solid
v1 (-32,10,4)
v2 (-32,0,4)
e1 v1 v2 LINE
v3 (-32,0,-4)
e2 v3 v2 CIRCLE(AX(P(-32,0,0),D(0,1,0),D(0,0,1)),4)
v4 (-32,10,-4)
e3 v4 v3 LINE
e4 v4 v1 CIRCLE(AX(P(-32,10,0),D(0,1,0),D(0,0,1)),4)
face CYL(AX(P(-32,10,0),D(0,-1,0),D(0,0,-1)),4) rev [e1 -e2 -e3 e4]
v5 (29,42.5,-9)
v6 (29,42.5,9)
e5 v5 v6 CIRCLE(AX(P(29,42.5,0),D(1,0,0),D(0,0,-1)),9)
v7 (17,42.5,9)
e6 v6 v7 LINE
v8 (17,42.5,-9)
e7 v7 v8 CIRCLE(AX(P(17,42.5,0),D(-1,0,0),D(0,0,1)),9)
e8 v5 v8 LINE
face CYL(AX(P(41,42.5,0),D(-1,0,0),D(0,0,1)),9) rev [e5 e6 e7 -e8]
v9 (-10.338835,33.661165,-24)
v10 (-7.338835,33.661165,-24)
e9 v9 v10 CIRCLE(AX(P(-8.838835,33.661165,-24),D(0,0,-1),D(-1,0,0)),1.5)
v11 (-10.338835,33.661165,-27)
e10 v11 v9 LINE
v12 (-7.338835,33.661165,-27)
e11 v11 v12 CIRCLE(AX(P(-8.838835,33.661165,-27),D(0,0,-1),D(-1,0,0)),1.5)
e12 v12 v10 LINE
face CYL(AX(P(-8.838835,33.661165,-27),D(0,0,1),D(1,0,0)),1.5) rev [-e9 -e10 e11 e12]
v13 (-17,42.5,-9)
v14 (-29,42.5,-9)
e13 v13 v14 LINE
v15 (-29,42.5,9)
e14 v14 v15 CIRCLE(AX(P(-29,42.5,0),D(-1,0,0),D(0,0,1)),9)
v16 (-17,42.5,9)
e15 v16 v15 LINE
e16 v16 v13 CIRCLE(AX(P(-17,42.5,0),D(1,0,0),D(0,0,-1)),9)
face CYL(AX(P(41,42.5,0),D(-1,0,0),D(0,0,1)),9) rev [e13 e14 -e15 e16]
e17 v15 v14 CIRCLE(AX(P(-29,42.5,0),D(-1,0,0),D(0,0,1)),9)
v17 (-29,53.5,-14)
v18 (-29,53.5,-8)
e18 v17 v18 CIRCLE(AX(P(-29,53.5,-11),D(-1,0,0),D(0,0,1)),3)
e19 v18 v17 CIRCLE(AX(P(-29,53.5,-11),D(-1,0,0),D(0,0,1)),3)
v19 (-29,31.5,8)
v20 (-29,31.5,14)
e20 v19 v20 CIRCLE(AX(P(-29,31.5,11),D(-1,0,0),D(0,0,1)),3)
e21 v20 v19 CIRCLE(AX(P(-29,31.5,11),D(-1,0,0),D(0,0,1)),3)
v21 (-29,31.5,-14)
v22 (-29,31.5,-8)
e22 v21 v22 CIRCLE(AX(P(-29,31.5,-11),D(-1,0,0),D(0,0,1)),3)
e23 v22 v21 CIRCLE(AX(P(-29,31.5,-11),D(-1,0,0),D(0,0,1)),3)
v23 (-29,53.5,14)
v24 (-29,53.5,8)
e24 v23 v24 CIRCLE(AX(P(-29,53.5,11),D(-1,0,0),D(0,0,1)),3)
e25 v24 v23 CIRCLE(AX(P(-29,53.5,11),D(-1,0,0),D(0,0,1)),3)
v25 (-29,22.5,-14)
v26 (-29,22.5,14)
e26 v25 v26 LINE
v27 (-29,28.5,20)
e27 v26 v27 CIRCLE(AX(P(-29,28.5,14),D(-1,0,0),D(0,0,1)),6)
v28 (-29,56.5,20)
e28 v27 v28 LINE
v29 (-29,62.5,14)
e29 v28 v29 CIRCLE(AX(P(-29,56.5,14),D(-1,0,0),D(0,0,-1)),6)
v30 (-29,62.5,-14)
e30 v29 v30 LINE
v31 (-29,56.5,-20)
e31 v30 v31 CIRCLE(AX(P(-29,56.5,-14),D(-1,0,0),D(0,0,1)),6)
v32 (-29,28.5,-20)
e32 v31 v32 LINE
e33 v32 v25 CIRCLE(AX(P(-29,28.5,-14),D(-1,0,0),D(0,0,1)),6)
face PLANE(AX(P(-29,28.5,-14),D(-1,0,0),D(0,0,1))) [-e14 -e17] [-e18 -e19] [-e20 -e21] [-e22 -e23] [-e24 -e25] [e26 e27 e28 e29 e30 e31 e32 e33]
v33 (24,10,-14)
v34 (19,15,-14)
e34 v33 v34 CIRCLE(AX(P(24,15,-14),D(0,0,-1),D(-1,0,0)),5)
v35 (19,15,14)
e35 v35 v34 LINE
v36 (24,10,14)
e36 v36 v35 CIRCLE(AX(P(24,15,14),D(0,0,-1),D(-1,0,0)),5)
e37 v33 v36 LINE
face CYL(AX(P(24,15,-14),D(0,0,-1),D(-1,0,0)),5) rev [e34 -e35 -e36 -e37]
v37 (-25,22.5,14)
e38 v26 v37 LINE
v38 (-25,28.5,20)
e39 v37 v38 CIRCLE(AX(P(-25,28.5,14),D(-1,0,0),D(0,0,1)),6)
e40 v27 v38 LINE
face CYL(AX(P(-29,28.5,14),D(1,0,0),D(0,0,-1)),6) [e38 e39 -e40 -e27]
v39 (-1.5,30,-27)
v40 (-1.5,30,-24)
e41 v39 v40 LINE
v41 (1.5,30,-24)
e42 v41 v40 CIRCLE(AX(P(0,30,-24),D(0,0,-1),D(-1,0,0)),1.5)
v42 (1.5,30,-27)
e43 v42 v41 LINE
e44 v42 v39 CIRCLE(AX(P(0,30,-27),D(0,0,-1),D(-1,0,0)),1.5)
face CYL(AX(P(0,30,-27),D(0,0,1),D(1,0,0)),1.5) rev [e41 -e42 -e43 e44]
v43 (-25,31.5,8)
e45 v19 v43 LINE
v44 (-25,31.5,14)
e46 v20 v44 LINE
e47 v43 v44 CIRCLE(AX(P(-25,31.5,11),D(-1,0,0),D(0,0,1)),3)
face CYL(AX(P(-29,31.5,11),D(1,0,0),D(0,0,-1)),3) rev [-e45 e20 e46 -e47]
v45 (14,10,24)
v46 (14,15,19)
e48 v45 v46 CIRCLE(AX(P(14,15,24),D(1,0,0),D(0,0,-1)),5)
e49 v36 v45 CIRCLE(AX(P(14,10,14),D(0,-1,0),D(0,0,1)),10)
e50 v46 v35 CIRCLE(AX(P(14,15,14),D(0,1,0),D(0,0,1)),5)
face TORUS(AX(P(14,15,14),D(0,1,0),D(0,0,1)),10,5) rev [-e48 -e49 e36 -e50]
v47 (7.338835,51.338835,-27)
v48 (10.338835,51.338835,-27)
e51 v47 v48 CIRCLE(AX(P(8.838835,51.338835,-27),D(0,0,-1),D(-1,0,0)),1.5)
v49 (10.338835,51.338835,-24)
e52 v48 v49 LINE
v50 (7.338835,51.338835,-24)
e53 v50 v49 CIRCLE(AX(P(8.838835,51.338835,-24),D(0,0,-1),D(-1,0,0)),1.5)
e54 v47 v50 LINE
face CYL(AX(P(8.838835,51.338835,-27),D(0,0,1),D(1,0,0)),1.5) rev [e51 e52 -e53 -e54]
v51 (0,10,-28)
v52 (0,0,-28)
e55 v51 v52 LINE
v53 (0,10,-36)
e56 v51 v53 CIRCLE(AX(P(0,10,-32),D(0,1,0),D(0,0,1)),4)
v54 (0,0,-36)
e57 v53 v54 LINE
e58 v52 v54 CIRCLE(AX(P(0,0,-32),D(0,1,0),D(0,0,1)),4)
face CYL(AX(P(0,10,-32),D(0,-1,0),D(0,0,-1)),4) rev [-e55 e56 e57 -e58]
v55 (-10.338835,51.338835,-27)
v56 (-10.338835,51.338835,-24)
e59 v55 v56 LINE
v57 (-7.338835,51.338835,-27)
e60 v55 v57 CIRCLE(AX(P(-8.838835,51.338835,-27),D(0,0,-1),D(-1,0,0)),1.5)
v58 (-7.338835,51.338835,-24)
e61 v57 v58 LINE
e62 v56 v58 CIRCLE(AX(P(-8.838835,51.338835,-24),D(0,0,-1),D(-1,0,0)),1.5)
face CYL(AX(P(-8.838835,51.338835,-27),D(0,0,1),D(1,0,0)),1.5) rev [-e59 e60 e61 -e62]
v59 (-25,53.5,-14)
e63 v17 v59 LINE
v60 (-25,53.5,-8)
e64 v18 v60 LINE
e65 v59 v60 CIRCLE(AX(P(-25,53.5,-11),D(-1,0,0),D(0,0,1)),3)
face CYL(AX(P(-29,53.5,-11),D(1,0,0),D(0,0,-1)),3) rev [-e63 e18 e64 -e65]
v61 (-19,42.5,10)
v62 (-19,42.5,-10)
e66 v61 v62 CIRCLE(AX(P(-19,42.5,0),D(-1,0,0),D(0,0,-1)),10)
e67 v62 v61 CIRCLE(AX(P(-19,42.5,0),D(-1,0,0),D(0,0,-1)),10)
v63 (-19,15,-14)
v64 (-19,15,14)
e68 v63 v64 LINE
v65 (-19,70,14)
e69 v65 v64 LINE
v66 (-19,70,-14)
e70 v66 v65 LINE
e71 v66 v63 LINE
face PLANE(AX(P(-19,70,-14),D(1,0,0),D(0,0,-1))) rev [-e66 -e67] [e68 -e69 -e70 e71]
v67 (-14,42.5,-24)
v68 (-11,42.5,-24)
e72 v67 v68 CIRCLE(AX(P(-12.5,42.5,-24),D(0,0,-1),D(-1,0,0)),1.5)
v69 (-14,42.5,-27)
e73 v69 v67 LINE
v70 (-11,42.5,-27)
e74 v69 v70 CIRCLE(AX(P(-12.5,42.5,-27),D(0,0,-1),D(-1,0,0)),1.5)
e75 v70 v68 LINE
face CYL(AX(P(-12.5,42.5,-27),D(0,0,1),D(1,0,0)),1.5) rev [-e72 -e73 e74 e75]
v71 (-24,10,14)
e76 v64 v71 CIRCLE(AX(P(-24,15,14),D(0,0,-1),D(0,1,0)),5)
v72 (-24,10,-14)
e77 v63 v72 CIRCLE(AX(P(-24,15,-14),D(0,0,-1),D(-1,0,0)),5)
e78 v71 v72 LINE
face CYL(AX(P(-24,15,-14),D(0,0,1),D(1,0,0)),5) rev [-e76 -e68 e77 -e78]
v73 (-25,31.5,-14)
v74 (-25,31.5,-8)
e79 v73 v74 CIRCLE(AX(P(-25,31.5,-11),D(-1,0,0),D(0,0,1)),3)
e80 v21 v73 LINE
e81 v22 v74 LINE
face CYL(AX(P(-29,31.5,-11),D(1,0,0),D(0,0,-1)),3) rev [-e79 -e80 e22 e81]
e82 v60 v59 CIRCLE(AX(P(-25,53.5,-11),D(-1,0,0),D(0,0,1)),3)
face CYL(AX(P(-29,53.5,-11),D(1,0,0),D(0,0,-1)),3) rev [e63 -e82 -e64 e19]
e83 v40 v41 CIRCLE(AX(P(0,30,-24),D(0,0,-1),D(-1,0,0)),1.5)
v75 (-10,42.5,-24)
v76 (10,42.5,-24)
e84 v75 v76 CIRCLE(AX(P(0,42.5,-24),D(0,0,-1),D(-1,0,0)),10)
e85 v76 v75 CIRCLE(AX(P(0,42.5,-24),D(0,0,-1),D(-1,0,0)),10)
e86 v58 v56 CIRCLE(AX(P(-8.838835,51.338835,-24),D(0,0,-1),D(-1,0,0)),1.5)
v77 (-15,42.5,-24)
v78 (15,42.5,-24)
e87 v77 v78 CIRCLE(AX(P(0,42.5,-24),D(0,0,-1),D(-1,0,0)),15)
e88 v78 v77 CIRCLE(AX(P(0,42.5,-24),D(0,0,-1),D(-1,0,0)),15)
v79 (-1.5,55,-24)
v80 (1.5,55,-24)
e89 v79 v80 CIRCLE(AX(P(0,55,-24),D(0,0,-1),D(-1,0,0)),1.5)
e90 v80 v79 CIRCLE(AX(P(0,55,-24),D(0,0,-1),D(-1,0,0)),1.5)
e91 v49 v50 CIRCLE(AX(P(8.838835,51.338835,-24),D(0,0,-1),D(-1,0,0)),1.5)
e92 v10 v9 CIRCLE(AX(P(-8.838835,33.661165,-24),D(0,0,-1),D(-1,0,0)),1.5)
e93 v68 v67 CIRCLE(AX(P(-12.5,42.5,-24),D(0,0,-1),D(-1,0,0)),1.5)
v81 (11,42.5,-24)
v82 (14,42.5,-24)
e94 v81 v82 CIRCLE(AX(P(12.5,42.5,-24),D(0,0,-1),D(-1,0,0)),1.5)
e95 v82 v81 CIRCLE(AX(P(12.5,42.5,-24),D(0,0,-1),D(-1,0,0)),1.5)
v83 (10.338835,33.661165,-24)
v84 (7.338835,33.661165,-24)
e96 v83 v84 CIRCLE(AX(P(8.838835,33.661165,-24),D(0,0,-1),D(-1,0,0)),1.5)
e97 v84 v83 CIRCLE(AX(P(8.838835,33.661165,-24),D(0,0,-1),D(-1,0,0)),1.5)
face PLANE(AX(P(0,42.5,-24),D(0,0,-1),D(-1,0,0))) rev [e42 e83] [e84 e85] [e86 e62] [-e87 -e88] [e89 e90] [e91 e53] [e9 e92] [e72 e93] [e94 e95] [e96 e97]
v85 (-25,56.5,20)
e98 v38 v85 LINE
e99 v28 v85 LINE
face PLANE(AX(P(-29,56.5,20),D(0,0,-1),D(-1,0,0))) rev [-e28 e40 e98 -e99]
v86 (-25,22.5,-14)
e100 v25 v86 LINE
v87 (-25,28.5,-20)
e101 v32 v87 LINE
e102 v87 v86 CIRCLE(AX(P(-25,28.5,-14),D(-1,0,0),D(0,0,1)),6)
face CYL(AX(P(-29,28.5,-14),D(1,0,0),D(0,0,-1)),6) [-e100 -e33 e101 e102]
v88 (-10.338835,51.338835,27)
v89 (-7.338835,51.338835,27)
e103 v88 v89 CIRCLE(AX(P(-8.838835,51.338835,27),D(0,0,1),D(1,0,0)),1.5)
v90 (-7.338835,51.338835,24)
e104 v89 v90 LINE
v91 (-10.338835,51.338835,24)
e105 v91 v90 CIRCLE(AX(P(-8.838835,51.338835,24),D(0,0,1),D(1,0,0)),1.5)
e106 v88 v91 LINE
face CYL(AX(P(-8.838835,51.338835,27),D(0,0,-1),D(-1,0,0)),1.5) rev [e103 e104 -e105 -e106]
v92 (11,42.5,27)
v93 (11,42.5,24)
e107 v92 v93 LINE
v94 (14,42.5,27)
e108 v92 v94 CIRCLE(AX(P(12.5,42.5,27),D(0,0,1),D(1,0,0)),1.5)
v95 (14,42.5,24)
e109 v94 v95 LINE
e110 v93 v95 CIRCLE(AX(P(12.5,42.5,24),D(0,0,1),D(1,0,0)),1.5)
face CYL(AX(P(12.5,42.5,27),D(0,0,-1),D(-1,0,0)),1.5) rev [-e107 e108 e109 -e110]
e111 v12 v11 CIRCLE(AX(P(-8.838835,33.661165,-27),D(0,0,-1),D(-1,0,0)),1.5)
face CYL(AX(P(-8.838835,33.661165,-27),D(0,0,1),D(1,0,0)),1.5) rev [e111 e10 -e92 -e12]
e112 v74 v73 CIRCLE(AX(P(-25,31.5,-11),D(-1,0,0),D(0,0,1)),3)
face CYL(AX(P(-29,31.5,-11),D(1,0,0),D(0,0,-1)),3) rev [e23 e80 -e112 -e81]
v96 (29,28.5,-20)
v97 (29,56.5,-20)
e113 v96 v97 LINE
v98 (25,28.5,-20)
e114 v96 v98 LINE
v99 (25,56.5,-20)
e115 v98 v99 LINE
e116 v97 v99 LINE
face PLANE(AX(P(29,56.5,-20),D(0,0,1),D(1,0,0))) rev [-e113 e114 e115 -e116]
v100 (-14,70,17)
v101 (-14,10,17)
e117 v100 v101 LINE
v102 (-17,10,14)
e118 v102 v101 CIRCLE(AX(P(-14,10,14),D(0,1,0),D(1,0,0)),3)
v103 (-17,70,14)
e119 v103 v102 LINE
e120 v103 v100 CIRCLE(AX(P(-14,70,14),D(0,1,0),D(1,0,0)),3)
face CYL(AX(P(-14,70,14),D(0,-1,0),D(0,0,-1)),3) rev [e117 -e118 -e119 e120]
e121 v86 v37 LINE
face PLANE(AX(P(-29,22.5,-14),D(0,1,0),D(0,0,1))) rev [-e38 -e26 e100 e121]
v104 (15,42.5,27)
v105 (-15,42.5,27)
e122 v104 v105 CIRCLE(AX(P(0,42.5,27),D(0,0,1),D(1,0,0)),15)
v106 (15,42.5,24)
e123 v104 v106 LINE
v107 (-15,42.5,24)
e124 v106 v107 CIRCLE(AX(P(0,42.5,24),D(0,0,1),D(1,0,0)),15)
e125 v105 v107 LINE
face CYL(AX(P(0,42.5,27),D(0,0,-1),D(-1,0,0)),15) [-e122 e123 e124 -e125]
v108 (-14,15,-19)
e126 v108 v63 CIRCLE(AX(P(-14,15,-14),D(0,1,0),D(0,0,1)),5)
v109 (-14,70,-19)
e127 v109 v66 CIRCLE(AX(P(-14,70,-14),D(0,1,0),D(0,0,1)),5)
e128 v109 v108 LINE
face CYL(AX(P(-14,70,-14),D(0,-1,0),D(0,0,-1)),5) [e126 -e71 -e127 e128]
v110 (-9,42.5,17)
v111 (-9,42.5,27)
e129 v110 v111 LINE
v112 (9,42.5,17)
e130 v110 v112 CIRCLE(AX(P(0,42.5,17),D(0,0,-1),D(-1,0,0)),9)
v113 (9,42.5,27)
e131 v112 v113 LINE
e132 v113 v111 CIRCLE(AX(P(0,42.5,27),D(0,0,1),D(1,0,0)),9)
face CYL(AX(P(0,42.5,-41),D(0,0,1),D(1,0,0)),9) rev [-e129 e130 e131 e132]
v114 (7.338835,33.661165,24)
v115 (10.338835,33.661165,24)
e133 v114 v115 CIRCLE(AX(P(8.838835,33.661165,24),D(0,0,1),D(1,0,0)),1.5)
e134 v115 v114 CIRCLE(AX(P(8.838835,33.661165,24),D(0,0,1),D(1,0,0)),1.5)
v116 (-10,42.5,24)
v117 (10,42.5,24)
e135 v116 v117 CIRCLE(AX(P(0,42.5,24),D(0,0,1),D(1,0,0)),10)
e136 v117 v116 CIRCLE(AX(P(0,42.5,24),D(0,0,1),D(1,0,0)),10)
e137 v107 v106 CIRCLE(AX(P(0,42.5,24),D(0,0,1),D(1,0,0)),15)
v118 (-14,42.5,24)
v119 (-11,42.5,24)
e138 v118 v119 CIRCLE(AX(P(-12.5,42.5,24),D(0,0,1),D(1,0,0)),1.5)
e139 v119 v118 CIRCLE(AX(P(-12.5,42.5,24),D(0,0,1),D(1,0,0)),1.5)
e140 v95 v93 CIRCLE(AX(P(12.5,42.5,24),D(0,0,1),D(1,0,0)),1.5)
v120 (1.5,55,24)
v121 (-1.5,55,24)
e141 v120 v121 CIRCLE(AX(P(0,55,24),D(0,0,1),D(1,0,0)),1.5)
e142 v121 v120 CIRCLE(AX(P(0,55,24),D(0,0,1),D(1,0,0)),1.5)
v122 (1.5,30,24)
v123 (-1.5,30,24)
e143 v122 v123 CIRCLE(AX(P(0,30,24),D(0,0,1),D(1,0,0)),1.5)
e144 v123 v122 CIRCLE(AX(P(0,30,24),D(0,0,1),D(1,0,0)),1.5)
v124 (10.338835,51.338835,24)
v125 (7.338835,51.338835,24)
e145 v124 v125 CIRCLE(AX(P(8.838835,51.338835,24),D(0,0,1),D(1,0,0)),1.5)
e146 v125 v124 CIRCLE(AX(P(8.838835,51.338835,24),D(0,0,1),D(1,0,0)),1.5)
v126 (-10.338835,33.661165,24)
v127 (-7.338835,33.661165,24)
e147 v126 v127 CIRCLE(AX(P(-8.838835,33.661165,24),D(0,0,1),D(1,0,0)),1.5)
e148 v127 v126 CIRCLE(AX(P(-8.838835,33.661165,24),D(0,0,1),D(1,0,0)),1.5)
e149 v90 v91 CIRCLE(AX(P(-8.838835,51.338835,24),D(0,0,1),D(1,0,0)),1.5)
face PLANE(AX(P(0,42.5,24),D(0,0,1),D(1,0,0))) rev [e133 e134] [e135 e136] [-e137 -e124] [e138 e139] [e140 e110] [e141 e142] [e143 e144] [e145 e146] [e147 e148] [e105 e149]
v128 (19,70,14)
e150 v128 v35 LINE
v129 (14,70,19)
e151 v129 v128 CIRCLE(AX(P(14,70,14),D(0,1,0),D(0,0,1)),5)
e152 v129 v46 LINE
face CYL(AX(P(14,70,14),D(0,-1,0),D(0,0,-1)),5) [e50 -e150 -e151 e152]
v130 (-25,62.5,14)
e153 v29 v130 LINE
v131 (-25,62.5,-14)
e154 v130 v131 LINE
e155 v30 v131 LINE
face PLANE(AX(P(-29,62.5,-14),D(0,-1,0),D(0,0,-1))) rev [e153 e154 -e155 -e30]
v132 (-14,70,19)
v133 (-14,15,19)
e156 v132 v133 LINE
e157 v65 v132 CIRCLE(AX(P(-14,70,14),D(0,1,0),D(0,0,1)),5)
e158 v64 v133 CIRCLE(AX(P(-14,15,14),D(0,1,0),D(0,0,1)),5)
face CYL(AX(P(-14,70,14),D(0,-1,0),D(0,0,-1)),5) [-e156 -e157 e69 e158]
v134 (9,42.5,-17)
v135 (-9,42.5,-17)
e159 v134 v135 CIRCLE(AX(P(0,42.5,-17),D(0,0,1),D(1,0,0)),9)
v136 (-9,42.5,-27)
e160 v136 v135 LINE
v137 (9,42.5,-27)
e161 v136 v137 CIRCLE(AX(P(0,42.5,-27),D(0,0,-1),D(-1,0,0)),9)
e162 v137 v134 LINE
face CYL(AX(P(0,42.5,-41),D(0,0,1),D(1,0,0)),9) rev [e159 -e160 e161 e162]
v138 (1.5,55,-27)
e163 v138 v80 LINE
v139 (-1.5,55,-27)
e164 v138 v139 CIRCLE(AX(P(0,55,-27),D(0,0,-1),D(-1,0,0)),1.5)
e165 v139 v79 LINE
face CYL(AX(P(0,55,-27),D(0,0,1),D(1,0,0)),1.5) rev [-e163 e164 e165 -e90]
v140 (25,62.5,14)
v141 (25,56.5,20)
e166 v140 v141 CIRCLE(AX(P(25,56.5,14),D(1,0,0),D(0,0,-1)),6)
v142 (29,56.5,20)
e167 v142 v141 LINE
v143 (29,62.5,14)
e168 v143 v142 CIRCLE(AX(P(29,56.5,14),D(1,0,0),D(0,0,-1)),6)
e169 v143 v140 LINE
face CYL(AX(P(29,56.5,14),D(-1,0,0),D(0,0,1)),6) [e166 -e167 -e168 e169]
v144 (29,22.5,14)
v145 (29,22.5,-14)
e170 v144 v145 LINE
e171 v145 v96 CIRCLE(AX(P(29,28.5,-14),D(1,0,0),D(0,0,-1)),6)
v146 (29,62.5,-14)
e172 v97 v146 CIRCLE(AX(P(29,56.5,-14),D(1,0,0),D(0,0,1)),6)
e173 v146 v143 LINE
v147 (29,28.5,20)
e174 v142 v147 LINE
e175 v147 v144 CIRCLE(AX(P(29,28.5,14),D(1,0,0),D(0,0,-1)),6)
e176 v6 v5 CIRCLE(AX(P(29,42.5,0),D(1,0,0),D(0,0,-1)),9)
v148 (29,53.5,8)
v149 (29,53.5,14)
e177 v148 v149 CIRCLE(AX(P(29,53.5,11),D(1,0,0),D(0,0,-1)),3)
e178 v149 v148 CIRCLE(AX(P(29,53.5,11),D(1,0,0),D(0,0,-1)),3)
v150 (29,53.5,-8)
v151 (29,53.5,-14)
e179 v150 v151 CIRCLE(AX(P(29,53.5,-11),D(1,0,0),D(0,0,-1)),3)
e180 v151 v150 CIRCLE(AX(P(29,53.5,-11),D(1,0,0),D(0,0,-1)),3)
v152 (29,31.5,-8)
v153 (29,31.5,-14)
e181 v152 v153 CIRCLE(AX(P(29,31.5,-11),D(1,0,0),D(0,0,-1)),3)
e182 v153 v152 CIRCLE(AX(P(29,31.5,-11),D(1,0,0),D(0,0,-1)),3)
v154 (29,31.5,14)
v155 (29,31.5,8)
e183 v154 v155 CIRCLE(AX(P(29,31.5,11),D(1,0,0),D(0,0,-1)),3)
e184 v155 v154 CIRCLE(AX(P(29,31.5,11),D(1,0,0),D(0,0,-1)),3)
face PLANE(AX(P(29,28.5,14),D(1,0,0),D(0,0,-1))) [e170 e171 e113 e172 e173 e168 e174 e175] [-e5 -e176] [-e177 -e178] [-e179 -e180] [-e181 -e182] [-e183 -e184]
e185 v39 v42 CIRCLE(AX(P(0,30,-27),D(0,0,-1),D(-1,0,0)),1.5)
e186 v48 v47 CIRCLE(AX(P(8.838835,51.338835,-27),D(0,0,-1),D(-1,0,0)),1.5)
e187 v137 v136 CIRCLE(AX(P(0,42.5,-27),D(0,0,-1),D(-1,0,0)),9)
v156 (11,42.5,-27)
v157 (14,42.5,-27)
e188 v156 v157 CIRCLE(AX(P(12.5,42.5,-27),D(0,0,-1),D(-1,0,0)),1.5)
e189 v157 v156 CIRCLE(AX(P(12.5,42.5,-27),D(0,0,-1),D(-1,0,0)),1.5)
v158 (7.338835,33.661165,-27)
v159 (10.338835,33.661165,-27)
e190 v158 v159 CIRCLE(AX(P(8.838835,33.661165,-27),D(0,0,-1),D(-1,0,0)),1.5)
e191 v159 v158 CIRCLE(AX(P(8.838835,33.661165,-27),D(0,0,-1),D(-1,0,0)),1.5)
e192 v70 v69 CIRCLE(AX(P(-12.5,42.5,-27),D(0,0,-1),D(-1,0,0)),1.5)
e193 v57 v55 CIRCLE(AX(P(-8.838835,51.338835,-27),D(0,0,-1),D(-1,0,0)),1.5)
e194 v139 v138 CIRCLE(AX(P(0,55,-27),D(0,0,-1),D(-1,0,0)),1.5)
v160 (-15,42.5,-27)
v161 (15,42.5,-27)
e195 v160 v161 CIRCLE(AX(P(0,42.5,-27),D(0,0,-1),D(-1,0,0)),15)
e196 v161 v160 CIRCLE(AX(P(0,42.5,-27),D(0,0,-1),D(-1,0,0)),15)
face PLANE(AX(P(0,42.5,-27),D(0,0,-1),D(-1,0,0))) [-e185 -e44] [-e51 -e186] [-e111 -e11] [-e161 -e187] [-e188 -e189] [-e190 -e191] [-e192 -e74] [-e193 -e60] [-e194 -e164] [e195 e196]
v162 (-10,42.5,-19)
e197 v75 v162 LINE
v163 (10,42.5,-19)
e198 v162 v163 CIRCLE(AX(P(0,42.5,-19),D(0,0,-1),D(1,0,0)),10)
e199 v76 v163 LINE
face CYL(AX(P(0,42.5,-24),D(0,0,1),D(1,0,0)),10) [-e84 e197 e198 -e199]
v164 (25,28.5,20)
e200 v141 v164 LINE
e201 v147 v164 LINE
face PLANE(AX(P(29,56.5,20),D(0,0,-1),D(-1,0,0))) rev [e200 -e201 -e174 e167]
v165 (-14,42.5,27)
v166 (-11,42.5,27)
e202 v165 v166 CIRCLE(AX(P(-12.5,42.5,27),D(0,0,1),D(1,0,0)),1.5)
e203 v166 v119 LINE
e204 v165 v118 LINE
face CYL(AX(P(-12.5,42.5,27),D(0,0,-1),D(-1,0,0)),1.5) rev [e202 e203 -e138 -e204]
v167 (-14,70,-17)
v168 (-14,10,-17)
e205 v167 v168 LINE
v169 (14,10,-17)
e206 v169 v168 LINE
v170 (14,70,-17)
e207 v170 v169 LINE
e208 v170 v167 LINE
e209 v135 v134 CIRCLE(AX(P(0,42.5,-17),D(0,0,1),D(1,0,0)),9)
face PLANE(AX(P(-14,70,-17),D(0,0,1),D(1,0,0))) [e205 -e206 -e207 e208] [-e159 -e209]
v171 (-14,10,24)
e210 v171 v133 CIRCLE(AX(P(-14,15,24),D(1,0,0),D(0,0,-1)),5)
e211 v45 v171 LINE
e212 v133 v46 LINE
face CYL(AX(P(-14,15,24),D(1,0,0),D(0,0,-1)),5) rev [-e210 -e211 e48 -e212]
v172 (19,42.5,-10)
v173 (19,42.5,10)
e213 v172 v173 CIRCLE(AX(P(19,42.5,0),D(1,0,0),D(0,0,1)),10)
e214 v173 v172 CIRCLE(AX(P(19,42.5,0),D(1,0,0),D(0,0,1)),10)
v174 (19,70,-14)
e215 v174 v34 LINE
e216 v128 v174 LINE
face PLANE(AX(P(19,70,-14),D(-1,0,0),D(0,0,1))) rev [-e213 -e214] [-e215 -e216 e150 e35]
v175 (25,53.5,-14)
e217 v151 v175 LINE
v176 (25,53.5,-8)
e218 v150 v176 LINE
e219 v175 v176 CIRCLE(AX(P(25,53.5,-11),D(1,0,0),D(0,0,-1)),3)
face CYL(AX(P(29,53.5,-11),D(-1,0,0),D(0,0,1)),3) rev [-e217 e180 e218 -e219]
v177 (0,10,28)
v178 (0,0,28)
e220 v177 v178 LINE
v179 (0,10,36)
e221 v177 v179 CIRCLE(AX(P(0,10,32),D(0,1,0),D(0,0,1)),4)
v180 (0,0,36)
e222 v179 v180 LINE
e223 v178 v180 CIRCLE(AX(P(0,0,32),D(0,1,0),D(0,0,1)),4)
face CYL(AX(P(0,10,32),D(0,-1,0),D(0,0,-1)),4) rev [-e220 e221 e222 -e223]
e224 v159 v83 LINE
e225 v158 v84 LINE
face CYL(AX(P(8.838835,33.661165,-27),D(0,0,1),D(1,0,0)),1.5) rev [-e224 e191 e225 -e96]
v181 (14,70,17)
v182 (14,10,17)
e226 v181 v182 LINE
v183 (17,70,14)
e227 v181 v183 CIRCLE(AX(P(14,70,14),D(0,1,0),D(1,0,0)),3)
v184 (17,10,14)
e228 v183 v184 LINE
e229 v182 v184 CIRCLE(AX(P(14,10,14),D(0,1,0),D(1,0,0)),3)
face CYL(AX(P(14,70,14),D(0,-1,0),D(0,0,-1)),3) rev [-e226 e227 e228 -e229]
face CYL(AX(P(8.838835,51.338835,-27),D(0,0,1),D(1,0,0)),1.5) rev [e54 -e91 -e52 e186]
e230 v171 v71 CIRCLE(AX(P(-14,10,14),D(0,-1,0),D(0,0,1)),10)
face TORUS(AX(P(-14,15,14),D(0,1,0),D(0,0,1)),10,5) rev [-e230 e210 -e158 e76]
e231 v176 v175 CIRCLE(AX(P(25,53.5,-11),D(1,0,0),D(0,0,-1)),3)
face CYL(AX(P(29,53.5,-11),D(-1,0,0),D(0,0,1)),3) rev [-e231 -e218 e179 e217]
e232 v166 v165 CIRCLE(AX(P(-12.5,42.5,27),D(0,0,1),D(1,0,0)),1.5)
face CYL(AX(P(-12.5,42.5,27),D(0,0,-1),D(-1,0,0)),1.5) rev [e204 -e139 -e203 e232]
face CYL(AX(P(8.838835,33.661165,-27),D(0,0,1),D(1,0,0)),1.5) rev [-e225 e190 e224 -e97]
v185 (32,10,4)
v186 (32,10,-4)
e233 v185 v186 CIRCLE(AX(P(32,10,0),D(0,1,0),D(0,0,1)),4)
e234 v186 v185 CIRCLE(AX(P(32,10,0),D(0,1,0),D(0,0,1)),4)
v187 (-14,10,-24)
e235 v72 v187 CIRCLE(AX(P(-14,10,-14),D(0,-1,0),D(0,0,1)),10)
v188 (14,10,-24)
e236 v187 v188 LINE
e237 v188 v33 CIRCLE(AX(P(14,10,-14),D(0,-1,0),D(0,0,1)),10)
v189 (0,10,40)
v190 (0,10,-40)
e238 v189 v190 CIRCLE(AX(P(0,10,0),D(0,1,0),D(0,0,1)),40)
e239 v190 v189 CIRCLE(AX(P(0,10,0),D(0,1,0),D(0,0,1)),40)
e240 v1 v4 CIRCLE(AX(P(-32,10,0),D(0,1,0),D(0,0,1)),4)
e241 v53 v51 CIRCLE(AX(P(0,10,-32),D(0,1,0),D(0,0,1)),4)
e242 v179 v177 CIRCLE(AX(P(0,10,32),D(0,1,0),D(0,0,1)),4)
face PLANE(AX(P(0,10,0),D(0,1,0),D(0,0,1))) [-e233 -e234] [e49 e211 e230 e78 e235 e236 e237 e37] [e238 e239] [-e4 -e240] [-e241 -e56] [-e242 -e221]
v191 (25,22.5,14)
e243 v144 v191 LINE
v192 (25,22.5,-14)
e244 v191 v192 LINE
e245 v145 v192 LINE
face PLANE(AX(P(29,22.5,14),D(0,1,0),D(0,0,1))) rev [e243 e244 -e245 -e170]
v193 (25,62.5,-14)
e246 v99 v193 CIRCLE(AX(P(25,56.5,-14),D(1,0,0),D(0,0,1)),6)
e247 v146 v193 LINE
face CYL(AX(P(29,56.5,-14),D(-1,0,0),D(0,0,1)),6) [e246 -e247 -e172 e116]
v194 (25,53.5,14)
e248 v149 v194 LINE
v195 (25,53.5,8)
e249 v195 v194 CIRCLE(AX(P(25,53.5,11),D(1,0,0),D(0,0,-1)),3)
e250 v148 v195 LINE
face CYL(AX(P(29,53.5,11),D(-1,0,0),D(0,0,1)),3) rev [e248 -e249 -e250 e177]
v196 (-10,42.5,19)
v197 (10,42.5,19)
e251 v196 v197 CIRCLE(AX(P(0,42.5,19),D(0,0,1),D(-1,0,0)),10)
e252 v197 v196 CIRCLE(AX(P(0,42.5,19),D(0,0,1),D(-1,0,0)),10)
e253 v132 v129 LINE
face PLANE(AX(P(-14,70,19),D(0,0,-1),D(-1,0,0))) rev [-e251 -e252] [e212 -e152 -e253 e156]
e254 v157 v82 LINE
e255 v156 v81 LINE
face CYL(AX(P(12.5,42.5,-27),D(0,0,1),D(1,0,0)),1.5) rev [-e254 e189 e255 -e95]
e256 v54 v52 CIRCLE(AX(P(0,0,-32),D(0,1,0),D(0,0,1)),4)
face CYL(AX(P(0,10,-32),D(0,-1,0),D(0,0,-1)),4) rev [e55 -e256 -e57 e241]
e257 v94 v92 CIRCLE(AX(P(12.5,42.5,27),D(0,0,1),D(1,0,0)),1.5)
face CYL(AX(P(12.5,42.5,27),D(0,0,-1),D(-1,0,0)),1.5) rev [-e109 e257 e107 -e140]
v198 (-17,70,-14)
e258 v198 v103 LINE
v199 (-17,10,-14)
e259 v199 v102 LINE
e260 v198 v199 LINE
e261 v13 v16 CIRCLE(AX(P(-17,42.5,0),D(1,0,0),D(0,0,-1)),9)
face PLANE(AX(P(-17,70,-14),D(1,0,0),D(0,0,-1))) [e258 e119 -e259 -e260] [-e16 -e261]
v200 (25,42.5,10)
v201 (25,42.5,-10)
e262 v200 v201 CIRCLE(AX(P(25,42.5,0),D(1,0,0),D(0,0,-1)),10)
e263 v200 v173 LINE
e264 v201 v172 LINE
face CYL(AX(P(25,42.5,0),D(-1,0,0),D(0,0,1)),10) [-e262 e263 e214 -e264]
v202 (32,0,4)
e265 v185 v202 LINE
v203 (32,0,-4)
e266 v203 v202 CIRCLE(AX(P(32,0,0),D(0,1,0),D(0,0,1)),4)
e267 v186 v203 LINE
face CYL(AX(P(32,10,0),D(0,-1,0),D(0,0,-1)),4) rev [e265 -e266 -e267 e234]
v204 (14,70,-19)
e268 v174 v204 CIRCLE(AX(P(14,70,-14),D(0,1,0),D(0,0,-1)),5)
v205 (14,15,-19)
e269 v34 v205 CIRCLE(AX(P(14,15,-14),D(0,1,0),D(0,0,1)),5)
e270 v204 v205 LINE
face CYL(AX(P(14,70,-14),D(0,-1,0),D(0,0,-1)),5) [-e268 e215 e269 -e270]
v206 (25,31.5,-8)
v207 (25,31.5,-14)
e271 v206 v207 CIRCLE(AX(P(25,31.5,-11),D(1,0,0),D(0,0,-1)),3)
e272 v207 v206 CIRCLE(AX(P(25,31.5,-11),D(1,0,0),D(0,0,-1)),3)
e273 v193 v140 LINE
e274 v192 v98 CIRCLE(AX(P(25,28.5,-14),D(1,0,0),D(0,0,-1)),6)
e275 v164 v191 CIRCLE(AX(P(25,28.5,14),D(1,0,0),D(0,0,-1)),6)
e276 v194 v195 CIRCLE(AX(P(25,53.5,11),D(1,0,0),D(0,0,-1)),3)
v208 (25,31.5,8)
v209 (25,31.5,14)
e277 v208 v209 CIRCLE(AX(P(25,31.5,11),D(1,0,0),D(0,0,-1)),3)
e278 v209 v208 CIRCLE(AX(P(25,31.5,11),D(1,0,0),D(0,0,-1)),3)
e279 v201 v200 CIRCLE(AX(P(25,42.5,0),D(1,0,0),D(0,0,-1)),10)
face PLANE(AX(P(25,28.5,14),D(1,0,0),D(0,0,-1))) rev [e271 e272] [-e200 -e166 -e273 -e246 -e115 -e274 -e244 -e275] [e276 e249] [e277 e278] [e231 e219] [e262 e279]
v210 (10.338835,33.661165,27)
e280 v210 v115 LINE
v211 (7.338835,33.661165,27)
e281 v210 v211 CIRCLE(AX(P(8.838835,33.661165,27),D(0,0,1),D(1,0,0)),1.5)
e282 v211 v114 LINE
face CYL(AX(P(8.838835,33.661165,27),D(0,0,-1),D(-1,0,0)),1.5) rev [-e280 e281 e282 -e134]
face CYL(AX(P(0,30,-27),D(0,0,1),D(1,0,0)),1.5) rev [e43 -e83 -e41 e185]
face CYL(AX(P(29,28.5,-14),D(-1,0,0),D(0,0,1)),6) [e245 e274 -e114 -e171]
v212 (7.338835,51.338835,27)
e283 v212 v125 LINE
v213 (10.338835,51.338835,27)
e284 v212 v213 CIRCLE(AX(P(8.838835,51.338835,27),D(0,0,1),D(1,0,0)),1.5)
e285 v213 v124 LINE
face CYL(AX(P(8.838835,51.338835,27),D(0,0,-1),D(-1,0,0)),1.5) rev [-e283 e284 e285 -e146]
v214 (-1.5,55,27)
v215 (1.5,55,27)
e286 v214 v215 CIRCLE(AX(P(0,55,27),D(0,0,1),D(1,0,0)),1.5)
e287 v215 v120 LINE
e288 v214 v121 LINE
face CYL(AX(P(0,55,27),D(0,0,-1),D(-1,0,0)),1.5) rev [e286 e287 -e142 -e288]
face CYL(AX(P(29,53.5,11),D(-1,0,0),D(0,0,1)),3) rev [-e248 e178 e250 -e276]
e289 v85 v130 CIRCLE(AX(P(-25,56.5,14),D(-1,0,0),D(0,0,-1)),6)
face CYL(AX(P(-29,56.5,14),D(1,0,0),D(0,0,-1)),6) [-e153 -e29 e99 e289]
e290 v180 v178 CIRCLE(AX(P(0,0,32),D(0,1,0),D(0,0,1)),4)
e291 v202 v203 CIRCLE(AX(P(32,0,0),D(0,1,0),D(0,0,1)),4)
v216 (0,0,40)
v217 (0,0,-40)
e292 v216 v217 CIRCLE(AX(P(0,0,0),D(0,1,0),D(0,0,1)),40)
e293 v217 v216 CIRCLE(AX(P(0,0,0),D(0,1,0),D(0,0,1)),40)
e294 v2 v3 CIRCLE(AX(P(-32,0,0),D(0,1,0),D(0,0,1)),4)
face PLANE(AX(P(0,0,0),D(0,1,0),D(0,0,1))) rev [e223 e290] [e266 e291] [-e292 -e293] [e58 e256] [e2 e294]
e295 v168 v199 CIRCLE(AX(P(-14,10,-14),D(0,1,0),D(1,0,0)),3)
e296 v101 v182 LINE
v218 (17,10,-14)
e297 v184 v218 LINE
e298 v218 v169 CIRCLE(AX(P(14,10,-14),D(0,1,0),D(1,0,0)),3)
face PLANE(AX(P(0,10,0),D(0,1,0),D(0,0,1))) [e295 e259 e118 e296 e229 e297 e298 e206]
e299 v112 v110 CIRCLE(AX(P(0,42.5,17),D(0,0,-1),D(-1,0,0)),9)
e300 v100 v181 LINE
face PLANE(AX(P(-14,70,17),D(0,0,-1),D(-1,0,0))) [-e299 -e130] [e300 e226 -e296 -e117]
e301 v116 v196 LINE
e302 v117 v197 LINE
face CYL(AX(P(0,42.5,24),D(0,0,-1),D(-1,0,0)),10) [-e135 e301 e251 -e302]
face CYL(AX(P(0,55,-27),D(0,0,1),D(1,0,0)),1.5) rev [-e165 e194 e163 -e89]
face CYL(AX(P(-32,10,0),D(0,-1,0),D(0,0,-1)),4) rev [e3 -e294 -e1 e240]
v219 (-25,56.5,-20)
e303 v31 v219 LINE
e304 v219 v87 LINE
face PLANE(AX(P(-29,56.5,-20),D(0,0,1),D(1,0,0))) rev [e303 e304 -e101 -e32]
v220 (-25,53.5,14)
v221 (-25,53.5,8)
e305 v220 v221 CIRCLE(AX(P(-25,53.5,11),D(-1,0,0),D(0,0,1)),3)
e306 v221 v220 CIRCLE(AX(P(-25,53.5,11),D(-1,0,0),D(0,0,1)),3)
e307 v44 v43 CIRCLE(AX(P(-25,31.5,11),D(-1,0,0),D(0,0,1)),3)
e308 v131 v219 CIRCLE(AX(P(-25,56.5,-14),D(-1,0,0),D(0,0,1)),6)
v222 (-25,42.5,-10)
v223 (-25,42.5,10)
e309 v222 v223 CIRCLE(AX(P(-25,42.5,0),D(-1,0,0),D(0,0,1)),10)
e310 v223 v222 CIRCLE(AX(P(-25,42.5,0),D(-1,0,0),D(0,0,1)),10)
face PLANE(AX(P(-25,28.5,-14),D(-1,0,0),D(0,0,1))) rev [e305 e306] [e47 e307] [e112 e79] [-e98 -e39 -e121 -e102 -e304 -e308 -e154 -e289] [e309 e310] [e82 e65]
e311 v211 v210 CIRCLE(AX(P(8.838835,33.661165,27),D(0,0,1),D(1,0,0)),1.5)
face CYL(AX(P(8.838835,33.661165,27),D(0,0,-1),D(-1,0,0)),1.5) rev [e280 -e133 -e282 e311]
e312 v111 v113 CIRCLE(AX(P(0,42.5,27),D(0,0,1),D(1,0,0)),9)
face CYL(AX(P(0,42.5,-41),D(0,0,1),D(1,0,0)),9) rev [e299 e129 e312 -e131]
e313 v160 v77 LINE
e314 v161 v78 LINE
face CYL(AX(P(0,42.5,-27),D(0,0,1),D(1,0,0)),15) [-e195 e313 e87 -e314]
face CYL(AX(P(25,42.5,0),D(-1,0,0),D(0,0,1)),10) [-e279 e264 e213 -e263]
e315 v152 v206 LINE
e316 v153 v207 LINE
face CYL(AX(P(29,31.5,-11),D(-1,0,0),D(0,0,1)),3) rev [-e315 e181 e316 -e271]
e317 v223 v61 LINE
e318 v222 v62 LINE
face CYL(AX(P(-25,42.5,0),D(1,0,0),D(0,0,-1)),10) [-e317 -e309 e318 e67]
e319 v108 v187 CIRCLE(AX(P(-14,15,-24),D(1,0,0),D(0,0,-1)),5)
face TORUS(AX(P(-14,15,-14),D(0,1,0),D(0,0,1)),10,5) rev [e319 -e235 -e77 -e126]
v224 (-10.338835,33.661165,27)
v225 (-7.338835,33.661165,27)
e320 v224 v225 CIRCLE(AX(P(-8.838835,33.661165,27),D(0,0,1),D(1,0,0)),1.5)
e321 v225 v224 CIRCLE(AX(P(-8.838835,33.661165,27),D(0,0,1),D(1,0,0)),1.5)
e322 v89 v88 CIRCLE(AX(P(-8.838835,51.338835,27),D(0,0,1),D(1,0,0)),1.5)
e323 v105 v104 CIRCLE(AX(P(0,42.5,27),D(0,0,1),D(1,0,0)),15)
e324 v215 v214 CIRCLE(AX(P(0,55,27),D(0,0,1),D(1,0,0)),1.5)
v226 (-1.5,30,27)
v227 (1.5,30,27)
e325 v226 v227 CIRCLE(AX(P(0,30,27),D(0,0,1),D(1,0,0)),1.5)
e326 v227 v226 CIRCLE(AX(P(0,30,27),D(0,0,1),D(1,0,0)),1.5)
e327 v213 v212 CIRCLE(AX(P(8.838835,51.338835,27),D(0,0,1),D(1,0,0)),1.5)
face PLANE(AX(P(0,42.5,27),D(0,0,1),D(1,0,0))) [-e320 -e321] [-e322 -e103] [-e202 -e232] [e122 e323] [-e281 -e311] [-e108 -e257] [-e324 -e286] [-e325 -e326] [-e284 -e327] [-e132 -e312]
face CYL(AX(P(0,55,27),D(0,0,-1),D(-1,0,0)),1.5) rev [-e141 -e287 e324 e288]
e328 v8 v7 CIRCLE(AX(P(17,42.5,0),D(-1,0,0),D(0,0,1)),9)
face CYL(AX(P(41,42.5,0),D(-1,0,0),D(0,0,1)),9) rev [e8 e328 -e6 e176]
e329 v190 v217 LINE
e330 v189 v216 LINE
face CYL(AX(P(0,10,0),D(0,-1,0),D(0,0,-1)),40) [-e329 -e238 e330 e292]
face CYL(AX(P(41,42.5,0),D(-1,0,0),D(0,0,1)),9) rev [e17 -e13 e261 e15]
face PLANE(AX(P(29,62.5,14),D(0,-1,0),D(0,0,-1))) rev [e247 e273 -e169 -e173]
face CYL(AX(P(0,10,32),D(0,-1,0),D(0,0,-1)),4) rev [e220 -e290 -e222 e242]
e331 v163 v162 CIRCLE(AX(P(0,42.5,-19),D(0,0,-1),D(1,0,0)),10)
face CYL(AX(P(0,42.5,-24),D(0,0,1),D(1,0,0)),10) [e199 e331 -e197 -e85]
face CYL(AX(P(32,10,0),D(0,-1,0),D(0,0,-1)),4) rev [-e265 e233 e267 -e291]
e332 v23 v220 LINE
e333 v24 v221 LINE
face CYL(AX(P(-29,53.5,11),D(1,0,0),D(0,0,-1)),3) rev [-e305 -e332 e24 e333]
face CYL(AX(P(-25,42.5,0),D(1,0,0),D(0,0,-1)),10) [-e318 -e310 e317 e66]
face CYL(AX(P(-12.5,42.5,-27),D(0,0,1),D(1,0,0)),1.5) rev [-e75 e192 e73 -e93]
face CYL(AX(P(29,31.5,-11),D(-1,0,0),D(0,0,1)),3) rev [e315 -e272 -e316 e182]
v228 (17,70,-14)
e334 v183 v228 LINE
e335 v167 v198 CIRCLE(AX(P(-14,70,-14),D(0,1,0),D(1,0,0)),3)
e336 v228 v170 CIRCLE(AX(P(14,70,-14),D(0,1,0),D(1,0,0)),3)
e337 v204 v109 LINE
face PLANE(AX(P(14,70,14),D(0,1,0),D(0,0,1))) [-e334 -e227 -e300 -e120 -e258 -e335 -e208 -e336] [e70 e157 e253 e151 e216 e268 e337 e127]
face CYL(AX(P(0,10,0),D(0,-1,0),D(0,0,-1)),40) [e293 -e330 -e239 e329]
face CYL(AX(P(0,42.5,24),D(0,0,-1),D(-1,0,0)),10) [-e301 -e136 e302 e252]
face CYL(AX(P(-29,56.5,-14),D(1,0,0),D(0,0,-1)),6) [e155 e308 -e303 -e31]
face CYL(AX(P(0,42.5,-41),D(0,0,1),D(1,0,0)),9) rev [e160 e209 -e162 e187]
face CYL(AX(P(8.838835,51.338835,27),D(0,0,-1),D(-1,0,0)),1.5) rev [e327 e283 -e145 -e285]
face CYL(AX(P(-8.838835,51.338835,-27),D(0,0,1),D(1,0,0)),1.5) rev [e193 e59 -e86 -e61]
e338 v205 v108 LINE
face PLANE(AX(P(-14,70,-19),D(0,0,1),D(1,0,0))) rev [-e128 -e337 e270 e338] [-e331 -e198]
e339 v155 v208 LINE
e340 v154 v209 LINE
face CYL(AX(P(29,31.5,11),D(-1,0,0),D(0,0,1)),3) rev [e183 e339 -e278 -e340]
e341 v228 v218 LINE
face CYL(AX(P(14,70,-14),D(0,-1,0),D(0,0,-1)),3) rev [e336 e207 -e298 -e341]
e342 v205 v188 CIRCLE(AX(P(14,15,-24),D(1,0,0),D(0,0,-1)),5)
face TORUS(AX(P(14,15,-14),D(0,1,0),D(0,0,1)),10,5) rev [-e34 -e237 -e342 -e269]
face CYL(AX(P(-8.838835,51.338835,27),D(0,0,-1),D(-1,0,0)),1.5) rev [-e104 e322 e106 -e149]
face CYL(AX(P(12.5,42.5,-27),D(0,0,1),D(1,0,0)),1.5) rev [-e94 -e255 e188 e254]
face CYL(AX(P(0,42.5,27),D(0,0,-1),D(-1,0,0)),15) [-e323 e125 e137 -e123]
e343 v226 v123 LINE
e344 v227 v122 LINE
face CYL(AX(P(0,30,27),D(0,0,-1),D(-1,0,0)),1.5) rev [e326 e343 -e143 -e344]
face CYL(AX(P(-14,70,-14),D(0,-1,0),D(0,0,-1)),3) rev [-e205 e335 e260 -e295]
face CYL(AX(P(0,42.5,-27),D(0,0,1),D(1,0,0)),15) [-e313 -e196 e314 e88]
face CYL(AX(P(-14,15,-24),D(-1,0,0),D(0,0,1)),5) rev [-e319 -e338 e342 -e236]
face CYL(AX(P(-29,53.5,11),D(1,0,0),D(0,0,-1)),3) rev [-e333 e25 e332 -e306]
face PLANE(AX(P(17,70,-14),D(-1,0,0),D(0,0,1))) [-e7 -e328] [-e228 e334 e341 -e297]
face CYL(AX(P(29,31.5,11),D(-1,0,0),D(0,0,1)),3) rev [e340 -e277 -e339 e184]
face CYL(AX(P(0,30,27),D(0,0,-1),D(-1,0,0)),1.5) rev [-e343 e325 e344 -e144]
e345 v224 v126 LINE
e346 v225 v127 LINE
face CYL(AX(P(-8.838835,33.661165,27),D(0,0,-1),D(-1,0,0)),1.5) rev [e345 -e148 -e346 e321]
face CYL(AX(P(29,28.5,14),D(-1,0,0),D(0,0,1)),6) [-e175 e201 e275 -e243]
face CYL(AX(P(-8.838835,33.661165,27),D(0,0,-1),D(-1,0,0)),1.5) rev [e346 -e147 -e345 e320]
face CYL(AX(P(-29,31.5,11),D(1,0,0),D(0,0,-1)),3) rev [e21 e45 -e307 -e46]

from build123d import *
from build123d.topology import SkipClean

# Parameters (mm, degrees)
BASE_FLANGE_SKETCH_R           = 40
BASE_FLANGE_SKETCH_R_2         = 4
BASE_FLANGE_80_DEPTH           = 10
SQUARE_BODY_38X38_WALL_2_DEPTH = 60
BODY_TO_FLANGE_FILLET_R5_R     = 5
CROSS_BORE_A_SKETCH_R          = 9
CROSS_BORE_A_18_DEPTH          = 60
CROSS_BORE_B_SKETCH_R          = 9
CROSS_BORE_B_18_DEPTH          = 60
PORT_START                     = 5
PORT_A1_STUB_SKETCH_R          = 10
PORT_A1_STUB_SKETCH_R_2        = 9
PORT_A1_STUB_18_DEPTH          = 5
ROUND_START                    = 3
ROUND_FLANGE_A1_SKETCH_R       = 15
ROUND_FLANGE_A1_SKETCH_R_2     = 9
ROUND_FLANGE_A1_SKETCH_R_3     = 1.5
ROUND_FLANGE_A1_30_DEPTH       = 3
PORT_A2_STUB_SKETCH_R          = 10
PORT_A2_STUB_SKETCH_R_2        = 9
PORT_A2_STUB_18_DEPTH          = 5
ROUND_FLANGE_A2_SKETCH_R       = 15
ROUND_FLANGE_A2_SKETCH_R_2     = 9
ROUND_FLANGE_A2_SKETCH_R_3     = 1.5
ROUND_FLANGE_A2_30_DEPTH       = 3
PORT_START_2                   = 6
PORT_B1_STUB_SKETCH_R          = 10
PORT_B1_STUB_SKETCH_R_2        = 9
PORT_B1_STUB_18_DEPTH          = 6
SQUARE_START                   = 4
SQUARE_FLANGE_B1_SKETCH_R      = 9
SQUARE_FLANGE_B1_SKETCH_R_2    = 3
SQUARE_FLANGE_B1_40X40_DEPTH   = 4
PORT_B2_STUB_SKETCH_R          = 10
PORT_B2_STUB_SKETCH_R_2        = 9
PORT_B2_STUB_18_DEPTH          = 6
SQUARE_FLANGE_B2_SKETCH_R      = 9
SQUARE_FLANGE_B2_SKETCH_R_2    = 3
SQUARE_FLANGE_B2_40X40_DEPTH   = 4


with BuildPart() as part:
    # Base Flange Sketch → Base Flange Ø80 (new body)
    with BuildSketch(Plane(origin=(0, 0, 0), x_dir=(1, 0, 0), z_dir=(0, 1, 0))):
        with Locations(Location((0, 0, 0), (0, 0, 270))):
            Circle(BASE_FLANGE_SKETCH_R)
        with Locations(Location((0, 32, 0), (0, 0, 270))):
            Circle(BASE_FLANGE_SKETCH_R_2, mode=Mode.SUBTRACT)
        with Locations(Location((32, 0, 0), (0, 0, 270))):
            Circle(BASE_FLANGE_SKETCH_R_2, mode=Mode.SUBTRACT)
        with Locations(Location((0, -32, 0), (0, 0, 270))):
            Circle(BASE_FLANGE_SKETCH_R_2, mode=Mode.SUBTRACT)
        with Locations(Location((-32, 0, 0), (0, 0, 270))):
            Circle(BASE_FLANGE_SKETCH_R_2, mode=Mode.SUBTRACT)
    extrude(amount=BASE_FLANGE_80_DEPTH)

    # Square Body Sketch → Square Body 38x38 Wall 2 (add)
    with BuildSketch(Plane(origin=(0, 10, 0), x_dir=(1, 0, 0), z_dir=(0, 1, 0))):
        with BuildLine():
            Line((19, 14), (19, -14))
            ThreePointArc((19, -14), (17.535533906, -17.535533906), (14, -19))
            Line((14, -19), (-14, -19))
            ThreePointArc((-14, -19), (-17.535533906, -17.535533906), (-19, -14))
            Line((-19, -14), (-19, 14))
            ThreePointArc((-19, 14), (-17.535533906, 17.535533906), (-14, 19))
            Line((-14, 19), (14, 19))
            ThreePointArc((14, 19), (17.535533906, 17.535533906), (19, 14))
        make_face()
        with BuildLine():
            Line((17, 14), (17, -14))
            ThreePointArc((17, -14), (16.121320344, -16.121320344), (14, -17))
            Line((14, -17), (-14, -17))
            ThreePointArc((-14, -17), (-16.121320344, -16.121320344), (-17, -14))
            Line((-17, -14), (-17, 14))
            ThreePointArc((-17, 14), (-16.121320344, 16.121320344), (-14, 17))
            Line((-14, 17), (14, 17))
            ThreePointArc((14, 17), (16.121320344, 16.121320344), (17, 14))
        make_face(mode=Mode.SUBTRACT)
    extrude(amount=SQUARE_BODY_38X38_WALL_2_DEPTH)

    # Body to Flange Fillet R5
    body_to_flange_fillet_r5_edges = [part.edges().sort_by_distance(p)[0] for p in [
        (17.535533906, 10, 17.535533906),
        (19, 10, 0),
        (17.535533906, 10, -17.535533906),
        (0, 10, -19),
        (-17.535533906, 10, -17.535533906),
        (-19, 10, 0),
        (-17.535533906, 10, 17.535533906),
        (0, 10, 19),
    ]]
    fillet(body_to_flange_fillet_r5_edges, radius=BODY_TO_FLANGE_FILLET_R5_R)

    # Cross Bore A Sketch → Cross Bore A Ø18 (cut)
    with BuildSketch(Plane.XY.offset(19)):
        with Locations((0, 42.5)):
            Circle(CROSS_BORE_A_SKETCH_R)
    extrude(amount=-CROSS_BORE_A_18_DEPTH, mode=Mode.SUBTRACT)

    # Cross Bore B Sketch → Cross Bore B Ø18 (cut)
    with BuildSketch(Plane.ZY.offset(19)):
        with Locations((0, 42.5)):
            Circle(CROSS_BORE_B_SKETCH_R)
    extrude(amount=-CROSS_BORE_B_18_DEPTH, mode=Mode.SUBTRACT)

    # Port A1 Stub Sketch → Port A1 Stub Ø18 (add)
    with BuildSketch(Plane.XY.offset(19).offset(PORT_START)):
        with Locations((0, 42.5)):
            Circle(PORT_A1_STUB_SKETCH_R)
        with Locations((0, 42.5)):
            Circle(PORT_A1_STUB_SKETCH_R_2, mode=Mode.SUBTRACT)
    extrude(amount=-PORT_A1_STUB_18_DEPTH)

    # Round Flange A1 Sketch → Round Flange A1 Ø30 (add)
    with BuildSketch(Plane.XY.offset(24).offset(ROUND_START)):
        with Locations((0, 42.5)):
            Circle(ROUND_FLANGE_A1_SKETCH_R)
        with Locations((0, 42.5)):
            Circle(ROUND_FLANGE_A1_SKETCH_R_2, mode=Mode.SUBTRACT)
        with Locations((0, 55)):
            Circle(ROUND_FLANGE_A1_SKETCH_R_3, mode=Mode.SUBTRACT)
        with Locations((8.838834765, 51.338834765)):
            Circle(ROUND_FLANGE_A1_SKETCH_R_3, mode=Mode.SUBTRACT)
        with Locations((12.5, 42.5)):
            Circle(ROUND_FLANGE_A1_SKETCH_R_3, mode=Mode.SUBTRACT)
        with Locations((8.838834765, 33.661165235)):
            Circle(ROUND_FLANGE_A1_SKETCH_R_3, mode=Mode.SUBTRACT)
        with Locations((0, 30)):
            Circle(ROUND_FLANGE_A1_SKETCH_R_3, mode=Mode.SUBTRACT)
        with Locations((-8.838834765, 33.661165235)):
            Circle(ROUND_FLANGE_A1_SKETCH_R_3, mode=Mode.SUBTRACT)
        with Locations((-12.5, 42.5)):
            Circle(ROUND_FLANGE_A1_SKETCH_R_3, mode=Mode.SUBTRACT)
        with Locations((-8.838834765, 51.338834765)):
            Circle(ROUND_FLANGE_A1_SKETCH_R_3, mode=Mode.SUBTRACT)
    extrude(amount=-ROUND_FLANGE_A1_30_DEPTH)

    # Port A2 Stub Sketch → Port A2 Stub Ø18 (add)
    with SkipClean():  # the faces are left unmerged after this step: merging them gives an invalid solid
        with BuildSketch(Plane(origin=(0, 0, -19), x_dir=(-1, 0, 0), z_dir=(0, 0, -1))):
            with Locations((0, 42.5)):
                Circle(PORT_A2_STUB_SKETCH_R)
            with Locations((0, 42.5)):
                Circle(PORT_A2_STUB_SKETCH_R_2, mode=Mode.SUBTRACT)
        extrude(amount=PORT_A2_STUB_18_DEPTH)

    # Round Flange A2 Sketch → Round Flange A2 Ø30 (add)
    with SkipClean():  # the faces are left unmerged after this step: merging them gives an invalid solid
        with BuildSketch(Plane(origin=(0, 0, -24), x_dir=(-1, 0, 0), z_dir=(0, 0, -1))):
            with Locations(Location((0, 42.5, 0), (0, 0, 180))):
                Circle(ROUND_FLANGE_A2_SKETCH_R)
            with Locations(Location((0, 42.5, 0), (0, 0, 180))):
                Circle(ROUND_FLANGE_A2_SKETCH_R_2, mode=Mode.SUBTRACT)
            with Locations(Location((0, 55, 0), (0, 0, 180))):
                Circle(ROUND_FLANGE_A2_SKETCH_R_3, mode=Mode.SUBTRACT)
            with Locations(Location((8.838834765, 51.338834765, 0), (0, 0, 180))):
                Circle(ROUND_FLANGE_A2_SKETCH_R_3, mode=Mode.SUBTRACT)
            with Locations(Location((12.5, 42.5, 0), (0, 0, 180))):
                Circle(ROUND_FLANGE_A2_SKETCH_R_3, mode=Mode.SUBTRACT)
            with Locations(Location((8.838834765, 33.661165235, 0), (0, 0, 180))):
                Circle(ROUND_FLANGE_A2_SKETCH_R_3, mode=Mode.SUBTRACT)
            with Locations(Location((0, 30, 0), (0, 0, 180))):
                Circle(ROUND_FLANGE_A2_SKETCH_R_3, mode=Mode.SUBTRACT)
            with Locations(Location((-8.838834765, 33.661165235, 0), (0, 0, 180))):
                Circle(ROUND_FLANGE_A2_SKETCH_R_3, mode=Mode.SUBTRACT)
            with Locations(Location((-12.5, 42.5, 0), (0, 0, 180))):
                Circle(ROUND_FLANGE_A2_SKETCH_R_3, mode=Mode.SUBTRACT)
            with Locations(Location((-8.838834765, 51.338834765, 0), (0, 0, 180))):
                Circle(ROUND_FLANGE_A2_SKETCH_R_3, mode=Mode.SUBTRACT)
        extrude(amount=ROUND_FLANGE_A2_30_DEPTH)

    # Port B1 Stub Sketch → Port B1 Stub Ø18 (add)
    with SkipClean():  # the faces are left unmerged after this step: merging them gives an invalid solid
        with BuildSketch(Plane.ZY.offset(19).offset(PORT_START_2)):
            with Locations((0, 42.5)):
                Circle(PORT_B1_STUB_SKETCH_R)
            with Locations((0, 42.5)):
                Circle(PORT_B1_STUB_SKETCH_R_2, mode=Mode.SUBTRACT)
        extrude(amount=-PORT_B1_STUB_18_DEPTH)

    # Square Flange B1 Sketch → Square Flange B1 40x40 (add)
    with SkipClean():  # the faces are left unmerged after this step: merging them gives an invalid solid
        with BuildSketch(Plane.ZY.offset(25).offset(SQUARE_START)):
            with BuildLine():
                Line((-14, 62.5), (14, 62.5))
                ThreePointArc((14, 62.5), (18.242640687, 60.742640687), (20, 56.5))
                Line((20, 56.5), (20, 28.5))
                ThreePointArc((20, 28.5), (18.242640687, 24.257359313), (14, 22.5))
                Line((14, 22.5), (-14, 22.5))
                ThreePointArc((-14, 22.5), (-18.242640687, 24.257359313), (-20, 28.5))
                Line((-20, 28.5), (-20, 56.5))
                ThreePointArc((-20, 56.5), (-18.242640687, 60.742640687), (-14, 62.5))
            make_face()
            with Locations((0, 42.5)):
                Circle(SQUARE_FLANGE_B1_SKETCH_R, mode=Mode.SUBTRACT)
            with Locations((-11, 53.5)):
                Circle(SQUARE_FLANGE_B1_SKETCH_R_2, mode=Mode.SUBTRACT)
            with Locations((11, 53.5)):
                Circle(SQUARE_FLANGE_B1_SKETCH_R_2, mode=Mode.SUBTRACT)
            with Locations((-11, 31.5)):
                Circle(SQUARE_FLANGE_B1_SKETCH_R_2, mode=Mode.SUBTRACT)
            with Locations((11, 31.5)):
                Circle(SQUARE_FLANGE_B1_SKETCH_R_2, mode=Mode.SUBTRACT)
        extrude(amount=-SQUARE_FLANGE_B1_40X40_DEPTH)

    # Port B2 Stub Sketch → Port B2 Stub Ø18 (add)
    with SkipClean():  # the faces are left unmerged after this step: merging them gives an invalid solid
        with BuildSketch(Plane(origin=(19, 0, 0), x_dir=(0, 0, -1), z_dir=(1, 0, 0))):
            with Locations((0, 42.5)):
                Circle(PORT_B2_STUB_SKETCH_R)
            with Locations((0, 42.5)):
                Circle(PORT_B2_STUB_SKETCH_R_2, mode=Mode.SUBTRACT)
        extrude(amount=PORT_B2_STUB_18_DEPTH)

    # Square Flange B2 Sketch → Square Flange B2 40x40 (add)
    with SkipClean():  # the faces are left unmerged after this step: merging them gives an invalid solid
        with BuildSketch(Plane(origin=(25, 0, 0), x_dir=(0, 0, -1), z_dir=(1, 0, 0))):
            with BuildLine():
                Line((-14, 62.5), (14, 62.5))
                ThreePointArc((14, 62.5), (18.242640687, 60.742640687), (20, 56.5))
                Line((20, 56.5), (20, 28.5))
                ThreePointArc((20, 28.5), (18.242640687, 24.257359313), (14, 22.5))
                Line((14, 22.5), (-14, 22.5))
                ThreePointArc((-14, 22.5), (-18.242640687, 24.257359313), (-20, 28.5))
                Line((-20, 28.5), (-20, 56.5))
                ThreePointArc((-20, 56.5), (-18.242640687, 60.742640687), (-14, 62.5))
            make_face()
            with Locations(Location((0, 42.5, 0), (0, 0, 180))):
                Circle(SQUARE_FLANGE_B2_SKETCH_R, mode=Mode.SUBTRACT)
            with Locations(Location((-11, 53.5, 0), (0, 0, 180))):
                Circle(SQUARE_FLANGE_B2_SKETCH_R_2, mode=Mode.SUBTRACT)
            with Locations(Location((-11, 31.5, 0), (0, 0, 180))):
                Circle(SQUARE_FLANGE_B2_SKETCH_R_2, mode=Mode.SUBTRACT)
            with Locations(Location((11, 31.5, 0), (0, 0, 180))):
                Circle(SQUARE_FLANGE_B2_SKETCH_R_2, mode=Mode.SUBTRACT)
            with Locations(Location((11, 53.5, 0), (0, 0, 180))):
                Circle(SQUARE_FLANGE_B2_SKETCH_R_2, mode=Mode.SUBTRACT)
        extrude(amount=SQUARE_FLANGE_B2_40X40_DEPTH)


solid = part.part
